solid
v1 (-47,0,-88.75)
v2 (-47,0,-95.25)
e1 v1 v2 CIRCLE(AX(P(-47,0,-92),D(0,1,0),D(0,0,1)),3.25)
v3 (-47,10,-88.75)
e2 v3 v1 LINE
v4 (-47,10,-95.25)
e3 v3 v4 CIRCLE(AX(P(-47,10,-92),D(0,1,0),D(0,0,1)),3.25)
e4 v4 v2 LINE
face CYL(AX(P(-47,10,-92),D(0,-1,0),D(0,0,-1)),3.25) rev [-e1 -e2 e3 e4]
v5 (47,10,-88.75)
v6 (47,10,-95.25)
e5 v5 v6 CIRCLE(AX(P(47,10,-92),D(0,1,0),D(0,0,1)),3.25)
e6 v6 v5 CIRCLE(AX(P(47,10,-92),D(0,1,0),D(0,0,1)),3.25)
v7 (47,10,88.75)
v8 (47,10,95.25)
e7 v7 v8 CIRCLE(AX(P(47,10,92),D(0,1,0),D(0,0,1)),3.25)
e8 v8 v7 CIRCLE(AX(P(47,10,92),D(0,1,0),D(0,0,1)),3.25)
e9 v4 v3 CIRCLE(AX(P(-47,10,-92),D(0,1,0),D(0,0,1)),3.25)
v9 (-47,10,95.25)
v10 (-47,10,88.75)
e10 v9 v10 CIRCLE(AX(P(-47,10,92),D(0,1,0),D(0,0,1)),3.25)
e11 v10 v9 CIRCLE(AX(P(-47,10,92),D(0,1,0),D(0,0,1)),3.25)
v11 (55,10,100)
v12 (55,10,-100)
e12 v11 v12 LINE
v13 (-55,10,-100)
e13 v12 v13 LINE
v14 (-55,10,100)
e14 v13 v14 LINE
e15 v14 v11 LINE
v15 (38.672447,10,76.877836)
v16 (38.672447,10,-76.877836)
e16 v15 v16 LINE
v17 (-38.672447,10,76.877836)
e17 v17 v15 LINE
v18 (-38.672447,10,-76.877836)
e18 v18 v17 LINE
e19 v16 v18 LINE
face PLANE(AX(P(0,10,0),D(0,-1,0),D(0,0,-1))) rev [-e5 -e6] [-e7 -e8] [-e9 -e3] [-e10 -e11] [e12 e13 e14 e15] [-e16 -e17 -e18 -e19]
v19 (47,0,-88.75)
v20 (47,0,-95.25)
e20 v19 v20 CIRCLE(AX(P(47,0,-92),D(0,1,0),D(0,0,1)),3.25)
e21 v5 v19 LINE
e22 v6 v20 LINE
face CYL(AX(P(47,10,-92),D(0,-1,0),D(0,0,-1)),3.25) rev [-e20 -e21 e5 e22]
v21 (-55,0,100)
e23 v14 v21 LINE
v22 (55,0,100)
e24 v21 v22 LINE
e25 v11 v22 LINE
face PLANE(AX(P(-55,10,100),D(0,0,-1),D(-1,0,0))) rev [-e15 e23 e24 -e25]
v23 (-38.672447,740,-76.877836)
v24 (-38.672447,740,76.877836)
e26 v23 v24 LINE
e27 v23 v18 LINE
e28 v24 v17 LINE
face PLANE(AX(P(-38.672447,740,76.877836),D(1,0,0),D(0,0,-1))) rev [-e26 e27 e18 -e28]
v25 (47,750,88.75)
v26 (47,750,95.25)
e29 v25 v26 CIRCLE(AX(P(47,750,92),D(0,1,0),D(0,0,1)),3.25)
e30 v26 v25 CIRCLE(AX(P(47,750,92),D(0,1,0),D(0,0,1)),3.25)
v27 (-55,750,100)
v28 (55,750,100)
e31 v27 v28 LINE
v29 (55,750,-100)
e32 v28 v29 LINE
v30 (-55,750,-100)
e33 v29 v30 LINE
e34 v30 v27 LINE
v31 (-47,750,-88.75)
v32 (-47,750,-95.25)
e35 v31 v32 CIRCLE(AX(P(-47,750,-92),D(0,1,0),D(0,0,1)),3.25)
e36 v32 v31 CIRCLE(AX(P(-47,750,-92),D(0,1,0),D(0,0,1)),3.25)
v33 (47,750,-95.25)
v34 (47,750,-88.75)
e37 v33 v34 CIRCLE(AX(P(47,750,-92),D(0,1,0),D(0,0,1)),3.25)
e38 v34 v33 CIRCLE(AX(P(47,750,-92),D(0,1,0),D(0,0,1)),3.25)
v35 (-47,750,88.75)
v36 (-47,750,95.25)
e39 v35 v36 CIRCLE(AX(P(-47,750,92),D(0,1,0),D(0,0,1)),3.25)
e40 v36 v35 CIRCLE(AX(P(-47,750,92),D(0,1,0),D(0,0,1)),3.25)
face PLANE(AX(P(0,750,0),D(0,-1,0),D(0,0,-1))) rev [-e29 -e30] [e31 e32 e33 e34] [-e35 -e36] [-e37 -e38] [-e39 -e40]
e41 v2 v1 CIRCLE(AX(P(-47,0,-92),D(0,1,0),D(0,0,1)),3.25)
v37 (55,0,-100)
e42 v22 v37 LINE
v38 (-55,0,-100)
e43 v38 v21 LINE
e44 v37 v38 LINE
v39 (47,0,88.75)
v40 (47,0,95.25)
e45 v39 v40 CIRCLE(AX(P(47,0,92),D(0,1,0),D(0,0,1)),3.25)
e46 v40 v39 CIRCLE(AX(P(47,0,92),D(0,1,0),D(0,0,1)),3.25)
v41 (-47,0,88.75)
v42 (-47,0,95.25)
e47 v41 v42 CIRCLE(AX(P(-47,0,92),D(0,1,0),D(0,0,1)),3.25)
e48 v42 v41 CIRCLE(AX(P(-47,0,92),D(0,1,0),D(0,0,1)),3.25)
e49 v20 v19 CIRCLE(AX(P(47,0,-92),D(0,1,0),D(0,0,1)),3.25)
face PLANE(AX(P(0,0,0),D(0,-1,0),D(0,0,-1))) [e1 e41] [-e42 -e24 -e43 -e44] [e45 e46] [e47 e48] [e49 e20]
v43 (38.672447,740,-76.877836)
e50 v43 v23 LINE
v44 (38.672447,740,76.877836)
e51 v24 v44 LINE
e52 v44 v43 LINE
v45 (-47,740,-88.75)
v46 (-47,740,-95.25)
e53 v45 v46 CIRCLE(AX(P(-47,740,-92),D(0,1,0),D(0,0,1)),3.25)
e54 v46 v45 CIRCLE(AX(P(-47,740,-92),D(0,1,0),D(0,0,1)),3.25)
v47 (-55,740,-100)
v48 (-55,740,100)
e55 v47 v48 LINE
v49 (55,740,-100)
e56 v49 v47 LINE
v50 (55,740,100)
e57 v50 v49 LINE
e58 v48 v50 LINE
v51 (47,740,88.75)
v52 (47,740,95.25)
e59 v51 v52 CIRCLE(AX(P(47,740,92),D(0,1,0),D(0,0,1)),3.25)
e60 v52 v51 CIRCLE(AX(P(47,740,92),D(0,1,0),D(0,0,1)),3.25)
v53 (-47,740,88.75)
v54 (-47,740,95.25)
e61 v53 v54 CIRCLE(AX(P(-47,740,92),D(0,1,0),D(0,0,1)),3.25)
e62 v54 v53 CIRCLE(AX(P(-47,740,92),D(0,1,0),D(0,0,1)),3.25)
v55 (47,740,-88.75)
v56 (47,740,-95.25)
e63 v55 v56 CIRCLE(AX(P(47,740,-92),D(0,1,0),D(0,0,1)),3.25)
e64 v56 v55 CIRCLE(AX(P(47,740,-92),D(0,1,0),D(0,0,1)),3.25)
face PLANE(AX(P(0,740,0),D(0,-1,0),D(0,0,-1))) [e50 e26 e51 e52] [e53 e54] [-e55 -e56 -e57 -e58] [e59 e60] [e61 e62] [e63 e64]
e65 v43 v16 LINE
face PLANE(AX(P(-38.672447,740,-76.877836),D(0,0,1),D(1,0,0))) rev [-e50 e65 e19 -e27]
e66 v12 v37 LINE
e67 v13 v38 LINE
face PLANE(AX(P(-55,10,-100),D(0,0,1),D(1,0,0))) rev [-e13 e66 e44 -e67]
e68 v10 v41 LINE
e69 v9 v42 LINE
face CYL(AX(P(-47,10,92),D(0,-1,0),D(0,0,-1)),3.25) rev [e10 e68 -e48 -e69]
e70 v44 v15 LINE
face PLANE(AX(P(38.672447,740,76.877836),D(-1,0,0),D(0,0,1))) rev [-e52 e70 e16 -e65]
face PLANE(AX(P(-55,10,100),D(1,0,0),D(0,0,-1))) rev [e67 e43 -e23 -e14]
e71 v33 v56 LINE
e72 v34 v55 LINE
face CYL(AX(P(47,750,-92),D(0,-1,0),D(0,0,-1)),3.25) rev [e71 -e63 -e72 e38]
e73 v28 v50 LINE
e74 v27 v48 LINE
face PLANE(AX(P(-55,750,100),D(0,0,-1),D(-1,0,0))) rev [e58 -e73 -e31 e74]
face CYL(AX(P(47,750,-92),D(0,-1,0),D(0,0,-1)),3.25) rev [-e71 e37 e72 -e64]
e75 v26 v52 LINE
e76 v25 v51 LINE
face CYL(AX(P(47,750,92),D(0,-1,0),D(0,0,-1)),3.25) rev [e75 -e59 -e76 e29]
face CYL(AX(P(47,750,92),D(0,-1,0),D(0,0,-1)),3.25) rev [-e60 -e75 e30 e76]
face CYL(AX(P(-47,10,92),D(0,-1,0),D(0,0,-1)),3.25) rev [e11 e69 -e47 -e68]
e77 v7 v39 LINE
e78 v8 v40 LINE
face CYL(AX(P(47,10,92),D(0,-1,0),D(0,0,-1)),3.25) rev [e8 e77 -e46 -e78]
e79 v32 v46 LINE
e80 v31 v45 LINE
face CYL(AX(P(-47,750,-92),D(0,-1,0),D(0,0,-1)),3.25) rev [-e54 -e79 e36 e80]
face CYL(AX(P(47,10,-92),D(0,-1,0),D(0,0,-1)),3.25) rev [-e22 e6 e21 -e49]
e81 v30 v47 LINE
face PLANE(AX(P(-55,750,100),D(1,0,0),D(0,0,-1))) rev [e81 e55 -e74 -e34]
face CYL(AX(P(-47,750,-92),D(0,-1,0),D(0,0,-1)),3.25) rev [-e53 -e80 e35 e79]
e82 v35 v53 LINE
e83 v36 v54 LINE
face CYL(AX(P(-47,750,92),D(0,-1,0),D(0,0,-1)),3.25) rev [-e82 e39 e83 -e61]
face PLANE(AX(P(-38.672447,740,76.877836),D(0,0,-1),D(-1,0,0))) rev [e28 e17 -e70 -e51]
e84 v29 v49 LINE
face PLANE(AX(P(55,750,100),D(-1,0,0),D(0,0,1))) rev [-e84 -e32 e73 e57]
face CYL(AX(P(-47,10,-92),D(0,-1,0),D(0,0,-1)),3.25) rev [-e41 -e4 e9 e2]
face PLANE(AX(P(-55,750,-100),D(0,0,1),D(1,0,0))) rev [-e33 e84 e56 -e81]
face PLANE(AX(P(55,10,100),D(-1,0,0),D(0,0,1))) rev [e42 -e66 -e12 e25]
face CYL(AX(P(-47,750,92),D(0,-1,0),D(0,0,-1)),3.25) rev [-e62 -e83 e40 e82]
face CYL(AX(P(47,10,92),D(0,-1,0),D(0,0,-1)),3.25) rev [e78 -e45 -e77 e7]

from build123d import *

# Parameters (mm, degrees)
SKETCH1_W           = 110
SKETCH1_H           = 200
SKETCH1_R           = 3.25
BOSS_EXTRUDE1_DEPTH = 10
SKETCH2_W           = 77.344894784
SKETCH2_H           = 153.75567248
BOSS_EXTRUDE2_DEPTH = 730
SKETCH4_W           = 110
SKETCH4_H           = 200
SKETCH4_R           = 3.25
BOSS_EXTRUDE4_DEPTH = 10


with BuildPart() as part:
    # Sketch1 → Boss-Extrude1 (new body)
    with BuildSketch(Plane(origin=(0, 0, 0), x_dir=(1, 0, 0), z_dir=(0, 1, 0))):
        Rectangle(SKETCH1_W, SKETCH1_H)
        with Locations(Location((-47, 92, 0), (0, 0, 270))):
            Circle(SKETCH1_R, mode=Mode.SUBTRACT)
        with Locations(Location((47, 92, 0), (0, 0, 270))):
            Circle(SKETCH1_R, mode=Mode.SUBTRACT)
        with Locations(Location((47, -92, 0), (0, 0, 270))):
            Circle(SKETCH1_R, mode=Mode.SUBTRACT)
        with Locations(Location((-47, -92, 0), (0, 0, 270))):
            Circle(SKETCH1_R, mode=Mode.SUBTRACT)
    extrude(amount=BOSS_EXTRUDE1_DEPTH)

    # Sketch2 → Boss-Extrude2 (add)
    with BuildSketch(Plane(origin=(0, 10, 0), x_dir=(1, 0, 0), z_dir=(0, 1, 0))):
        Rectangle(SKETCH2_W, SKETCH2_H)
    extrude(amount=BOSS_EXTRUDE2_DEPTH)

    # Sketch4 → Boss-Extrude4 (add)
    with BuildSketch(Plane(origin=(0, 740, 0), x_dir=(1, 0, 0), z_dir=(0, 1, 0))):
        Rectangle(SKETCH4_W, SKETCH4_H)
        with Locations(Location((-47, 92, 0), (0, 0, 270))):
            Circle(SKETCH4_R, mode=Mode.SUBTRACT)
        with Locations(Location((47, 92, 0), (0, 0, 270))):
            Circle(SKETCH4_R, mode=Mode.SUBTRACT)
        with Locations(Location((47, -92, 0), (0, 0, 270))):
            Circle(SKETCH4_R, mode=Mode.SUBTRACT)
        with Locations(Location((-47, -92, 0), (0, 0, 270))):
            Circle(SKETCH4_R, mode=Mode.SUBTRACT)
    extrude(amount=BOSS_EXTRUDE4_DEPTH)


solid = part.part
